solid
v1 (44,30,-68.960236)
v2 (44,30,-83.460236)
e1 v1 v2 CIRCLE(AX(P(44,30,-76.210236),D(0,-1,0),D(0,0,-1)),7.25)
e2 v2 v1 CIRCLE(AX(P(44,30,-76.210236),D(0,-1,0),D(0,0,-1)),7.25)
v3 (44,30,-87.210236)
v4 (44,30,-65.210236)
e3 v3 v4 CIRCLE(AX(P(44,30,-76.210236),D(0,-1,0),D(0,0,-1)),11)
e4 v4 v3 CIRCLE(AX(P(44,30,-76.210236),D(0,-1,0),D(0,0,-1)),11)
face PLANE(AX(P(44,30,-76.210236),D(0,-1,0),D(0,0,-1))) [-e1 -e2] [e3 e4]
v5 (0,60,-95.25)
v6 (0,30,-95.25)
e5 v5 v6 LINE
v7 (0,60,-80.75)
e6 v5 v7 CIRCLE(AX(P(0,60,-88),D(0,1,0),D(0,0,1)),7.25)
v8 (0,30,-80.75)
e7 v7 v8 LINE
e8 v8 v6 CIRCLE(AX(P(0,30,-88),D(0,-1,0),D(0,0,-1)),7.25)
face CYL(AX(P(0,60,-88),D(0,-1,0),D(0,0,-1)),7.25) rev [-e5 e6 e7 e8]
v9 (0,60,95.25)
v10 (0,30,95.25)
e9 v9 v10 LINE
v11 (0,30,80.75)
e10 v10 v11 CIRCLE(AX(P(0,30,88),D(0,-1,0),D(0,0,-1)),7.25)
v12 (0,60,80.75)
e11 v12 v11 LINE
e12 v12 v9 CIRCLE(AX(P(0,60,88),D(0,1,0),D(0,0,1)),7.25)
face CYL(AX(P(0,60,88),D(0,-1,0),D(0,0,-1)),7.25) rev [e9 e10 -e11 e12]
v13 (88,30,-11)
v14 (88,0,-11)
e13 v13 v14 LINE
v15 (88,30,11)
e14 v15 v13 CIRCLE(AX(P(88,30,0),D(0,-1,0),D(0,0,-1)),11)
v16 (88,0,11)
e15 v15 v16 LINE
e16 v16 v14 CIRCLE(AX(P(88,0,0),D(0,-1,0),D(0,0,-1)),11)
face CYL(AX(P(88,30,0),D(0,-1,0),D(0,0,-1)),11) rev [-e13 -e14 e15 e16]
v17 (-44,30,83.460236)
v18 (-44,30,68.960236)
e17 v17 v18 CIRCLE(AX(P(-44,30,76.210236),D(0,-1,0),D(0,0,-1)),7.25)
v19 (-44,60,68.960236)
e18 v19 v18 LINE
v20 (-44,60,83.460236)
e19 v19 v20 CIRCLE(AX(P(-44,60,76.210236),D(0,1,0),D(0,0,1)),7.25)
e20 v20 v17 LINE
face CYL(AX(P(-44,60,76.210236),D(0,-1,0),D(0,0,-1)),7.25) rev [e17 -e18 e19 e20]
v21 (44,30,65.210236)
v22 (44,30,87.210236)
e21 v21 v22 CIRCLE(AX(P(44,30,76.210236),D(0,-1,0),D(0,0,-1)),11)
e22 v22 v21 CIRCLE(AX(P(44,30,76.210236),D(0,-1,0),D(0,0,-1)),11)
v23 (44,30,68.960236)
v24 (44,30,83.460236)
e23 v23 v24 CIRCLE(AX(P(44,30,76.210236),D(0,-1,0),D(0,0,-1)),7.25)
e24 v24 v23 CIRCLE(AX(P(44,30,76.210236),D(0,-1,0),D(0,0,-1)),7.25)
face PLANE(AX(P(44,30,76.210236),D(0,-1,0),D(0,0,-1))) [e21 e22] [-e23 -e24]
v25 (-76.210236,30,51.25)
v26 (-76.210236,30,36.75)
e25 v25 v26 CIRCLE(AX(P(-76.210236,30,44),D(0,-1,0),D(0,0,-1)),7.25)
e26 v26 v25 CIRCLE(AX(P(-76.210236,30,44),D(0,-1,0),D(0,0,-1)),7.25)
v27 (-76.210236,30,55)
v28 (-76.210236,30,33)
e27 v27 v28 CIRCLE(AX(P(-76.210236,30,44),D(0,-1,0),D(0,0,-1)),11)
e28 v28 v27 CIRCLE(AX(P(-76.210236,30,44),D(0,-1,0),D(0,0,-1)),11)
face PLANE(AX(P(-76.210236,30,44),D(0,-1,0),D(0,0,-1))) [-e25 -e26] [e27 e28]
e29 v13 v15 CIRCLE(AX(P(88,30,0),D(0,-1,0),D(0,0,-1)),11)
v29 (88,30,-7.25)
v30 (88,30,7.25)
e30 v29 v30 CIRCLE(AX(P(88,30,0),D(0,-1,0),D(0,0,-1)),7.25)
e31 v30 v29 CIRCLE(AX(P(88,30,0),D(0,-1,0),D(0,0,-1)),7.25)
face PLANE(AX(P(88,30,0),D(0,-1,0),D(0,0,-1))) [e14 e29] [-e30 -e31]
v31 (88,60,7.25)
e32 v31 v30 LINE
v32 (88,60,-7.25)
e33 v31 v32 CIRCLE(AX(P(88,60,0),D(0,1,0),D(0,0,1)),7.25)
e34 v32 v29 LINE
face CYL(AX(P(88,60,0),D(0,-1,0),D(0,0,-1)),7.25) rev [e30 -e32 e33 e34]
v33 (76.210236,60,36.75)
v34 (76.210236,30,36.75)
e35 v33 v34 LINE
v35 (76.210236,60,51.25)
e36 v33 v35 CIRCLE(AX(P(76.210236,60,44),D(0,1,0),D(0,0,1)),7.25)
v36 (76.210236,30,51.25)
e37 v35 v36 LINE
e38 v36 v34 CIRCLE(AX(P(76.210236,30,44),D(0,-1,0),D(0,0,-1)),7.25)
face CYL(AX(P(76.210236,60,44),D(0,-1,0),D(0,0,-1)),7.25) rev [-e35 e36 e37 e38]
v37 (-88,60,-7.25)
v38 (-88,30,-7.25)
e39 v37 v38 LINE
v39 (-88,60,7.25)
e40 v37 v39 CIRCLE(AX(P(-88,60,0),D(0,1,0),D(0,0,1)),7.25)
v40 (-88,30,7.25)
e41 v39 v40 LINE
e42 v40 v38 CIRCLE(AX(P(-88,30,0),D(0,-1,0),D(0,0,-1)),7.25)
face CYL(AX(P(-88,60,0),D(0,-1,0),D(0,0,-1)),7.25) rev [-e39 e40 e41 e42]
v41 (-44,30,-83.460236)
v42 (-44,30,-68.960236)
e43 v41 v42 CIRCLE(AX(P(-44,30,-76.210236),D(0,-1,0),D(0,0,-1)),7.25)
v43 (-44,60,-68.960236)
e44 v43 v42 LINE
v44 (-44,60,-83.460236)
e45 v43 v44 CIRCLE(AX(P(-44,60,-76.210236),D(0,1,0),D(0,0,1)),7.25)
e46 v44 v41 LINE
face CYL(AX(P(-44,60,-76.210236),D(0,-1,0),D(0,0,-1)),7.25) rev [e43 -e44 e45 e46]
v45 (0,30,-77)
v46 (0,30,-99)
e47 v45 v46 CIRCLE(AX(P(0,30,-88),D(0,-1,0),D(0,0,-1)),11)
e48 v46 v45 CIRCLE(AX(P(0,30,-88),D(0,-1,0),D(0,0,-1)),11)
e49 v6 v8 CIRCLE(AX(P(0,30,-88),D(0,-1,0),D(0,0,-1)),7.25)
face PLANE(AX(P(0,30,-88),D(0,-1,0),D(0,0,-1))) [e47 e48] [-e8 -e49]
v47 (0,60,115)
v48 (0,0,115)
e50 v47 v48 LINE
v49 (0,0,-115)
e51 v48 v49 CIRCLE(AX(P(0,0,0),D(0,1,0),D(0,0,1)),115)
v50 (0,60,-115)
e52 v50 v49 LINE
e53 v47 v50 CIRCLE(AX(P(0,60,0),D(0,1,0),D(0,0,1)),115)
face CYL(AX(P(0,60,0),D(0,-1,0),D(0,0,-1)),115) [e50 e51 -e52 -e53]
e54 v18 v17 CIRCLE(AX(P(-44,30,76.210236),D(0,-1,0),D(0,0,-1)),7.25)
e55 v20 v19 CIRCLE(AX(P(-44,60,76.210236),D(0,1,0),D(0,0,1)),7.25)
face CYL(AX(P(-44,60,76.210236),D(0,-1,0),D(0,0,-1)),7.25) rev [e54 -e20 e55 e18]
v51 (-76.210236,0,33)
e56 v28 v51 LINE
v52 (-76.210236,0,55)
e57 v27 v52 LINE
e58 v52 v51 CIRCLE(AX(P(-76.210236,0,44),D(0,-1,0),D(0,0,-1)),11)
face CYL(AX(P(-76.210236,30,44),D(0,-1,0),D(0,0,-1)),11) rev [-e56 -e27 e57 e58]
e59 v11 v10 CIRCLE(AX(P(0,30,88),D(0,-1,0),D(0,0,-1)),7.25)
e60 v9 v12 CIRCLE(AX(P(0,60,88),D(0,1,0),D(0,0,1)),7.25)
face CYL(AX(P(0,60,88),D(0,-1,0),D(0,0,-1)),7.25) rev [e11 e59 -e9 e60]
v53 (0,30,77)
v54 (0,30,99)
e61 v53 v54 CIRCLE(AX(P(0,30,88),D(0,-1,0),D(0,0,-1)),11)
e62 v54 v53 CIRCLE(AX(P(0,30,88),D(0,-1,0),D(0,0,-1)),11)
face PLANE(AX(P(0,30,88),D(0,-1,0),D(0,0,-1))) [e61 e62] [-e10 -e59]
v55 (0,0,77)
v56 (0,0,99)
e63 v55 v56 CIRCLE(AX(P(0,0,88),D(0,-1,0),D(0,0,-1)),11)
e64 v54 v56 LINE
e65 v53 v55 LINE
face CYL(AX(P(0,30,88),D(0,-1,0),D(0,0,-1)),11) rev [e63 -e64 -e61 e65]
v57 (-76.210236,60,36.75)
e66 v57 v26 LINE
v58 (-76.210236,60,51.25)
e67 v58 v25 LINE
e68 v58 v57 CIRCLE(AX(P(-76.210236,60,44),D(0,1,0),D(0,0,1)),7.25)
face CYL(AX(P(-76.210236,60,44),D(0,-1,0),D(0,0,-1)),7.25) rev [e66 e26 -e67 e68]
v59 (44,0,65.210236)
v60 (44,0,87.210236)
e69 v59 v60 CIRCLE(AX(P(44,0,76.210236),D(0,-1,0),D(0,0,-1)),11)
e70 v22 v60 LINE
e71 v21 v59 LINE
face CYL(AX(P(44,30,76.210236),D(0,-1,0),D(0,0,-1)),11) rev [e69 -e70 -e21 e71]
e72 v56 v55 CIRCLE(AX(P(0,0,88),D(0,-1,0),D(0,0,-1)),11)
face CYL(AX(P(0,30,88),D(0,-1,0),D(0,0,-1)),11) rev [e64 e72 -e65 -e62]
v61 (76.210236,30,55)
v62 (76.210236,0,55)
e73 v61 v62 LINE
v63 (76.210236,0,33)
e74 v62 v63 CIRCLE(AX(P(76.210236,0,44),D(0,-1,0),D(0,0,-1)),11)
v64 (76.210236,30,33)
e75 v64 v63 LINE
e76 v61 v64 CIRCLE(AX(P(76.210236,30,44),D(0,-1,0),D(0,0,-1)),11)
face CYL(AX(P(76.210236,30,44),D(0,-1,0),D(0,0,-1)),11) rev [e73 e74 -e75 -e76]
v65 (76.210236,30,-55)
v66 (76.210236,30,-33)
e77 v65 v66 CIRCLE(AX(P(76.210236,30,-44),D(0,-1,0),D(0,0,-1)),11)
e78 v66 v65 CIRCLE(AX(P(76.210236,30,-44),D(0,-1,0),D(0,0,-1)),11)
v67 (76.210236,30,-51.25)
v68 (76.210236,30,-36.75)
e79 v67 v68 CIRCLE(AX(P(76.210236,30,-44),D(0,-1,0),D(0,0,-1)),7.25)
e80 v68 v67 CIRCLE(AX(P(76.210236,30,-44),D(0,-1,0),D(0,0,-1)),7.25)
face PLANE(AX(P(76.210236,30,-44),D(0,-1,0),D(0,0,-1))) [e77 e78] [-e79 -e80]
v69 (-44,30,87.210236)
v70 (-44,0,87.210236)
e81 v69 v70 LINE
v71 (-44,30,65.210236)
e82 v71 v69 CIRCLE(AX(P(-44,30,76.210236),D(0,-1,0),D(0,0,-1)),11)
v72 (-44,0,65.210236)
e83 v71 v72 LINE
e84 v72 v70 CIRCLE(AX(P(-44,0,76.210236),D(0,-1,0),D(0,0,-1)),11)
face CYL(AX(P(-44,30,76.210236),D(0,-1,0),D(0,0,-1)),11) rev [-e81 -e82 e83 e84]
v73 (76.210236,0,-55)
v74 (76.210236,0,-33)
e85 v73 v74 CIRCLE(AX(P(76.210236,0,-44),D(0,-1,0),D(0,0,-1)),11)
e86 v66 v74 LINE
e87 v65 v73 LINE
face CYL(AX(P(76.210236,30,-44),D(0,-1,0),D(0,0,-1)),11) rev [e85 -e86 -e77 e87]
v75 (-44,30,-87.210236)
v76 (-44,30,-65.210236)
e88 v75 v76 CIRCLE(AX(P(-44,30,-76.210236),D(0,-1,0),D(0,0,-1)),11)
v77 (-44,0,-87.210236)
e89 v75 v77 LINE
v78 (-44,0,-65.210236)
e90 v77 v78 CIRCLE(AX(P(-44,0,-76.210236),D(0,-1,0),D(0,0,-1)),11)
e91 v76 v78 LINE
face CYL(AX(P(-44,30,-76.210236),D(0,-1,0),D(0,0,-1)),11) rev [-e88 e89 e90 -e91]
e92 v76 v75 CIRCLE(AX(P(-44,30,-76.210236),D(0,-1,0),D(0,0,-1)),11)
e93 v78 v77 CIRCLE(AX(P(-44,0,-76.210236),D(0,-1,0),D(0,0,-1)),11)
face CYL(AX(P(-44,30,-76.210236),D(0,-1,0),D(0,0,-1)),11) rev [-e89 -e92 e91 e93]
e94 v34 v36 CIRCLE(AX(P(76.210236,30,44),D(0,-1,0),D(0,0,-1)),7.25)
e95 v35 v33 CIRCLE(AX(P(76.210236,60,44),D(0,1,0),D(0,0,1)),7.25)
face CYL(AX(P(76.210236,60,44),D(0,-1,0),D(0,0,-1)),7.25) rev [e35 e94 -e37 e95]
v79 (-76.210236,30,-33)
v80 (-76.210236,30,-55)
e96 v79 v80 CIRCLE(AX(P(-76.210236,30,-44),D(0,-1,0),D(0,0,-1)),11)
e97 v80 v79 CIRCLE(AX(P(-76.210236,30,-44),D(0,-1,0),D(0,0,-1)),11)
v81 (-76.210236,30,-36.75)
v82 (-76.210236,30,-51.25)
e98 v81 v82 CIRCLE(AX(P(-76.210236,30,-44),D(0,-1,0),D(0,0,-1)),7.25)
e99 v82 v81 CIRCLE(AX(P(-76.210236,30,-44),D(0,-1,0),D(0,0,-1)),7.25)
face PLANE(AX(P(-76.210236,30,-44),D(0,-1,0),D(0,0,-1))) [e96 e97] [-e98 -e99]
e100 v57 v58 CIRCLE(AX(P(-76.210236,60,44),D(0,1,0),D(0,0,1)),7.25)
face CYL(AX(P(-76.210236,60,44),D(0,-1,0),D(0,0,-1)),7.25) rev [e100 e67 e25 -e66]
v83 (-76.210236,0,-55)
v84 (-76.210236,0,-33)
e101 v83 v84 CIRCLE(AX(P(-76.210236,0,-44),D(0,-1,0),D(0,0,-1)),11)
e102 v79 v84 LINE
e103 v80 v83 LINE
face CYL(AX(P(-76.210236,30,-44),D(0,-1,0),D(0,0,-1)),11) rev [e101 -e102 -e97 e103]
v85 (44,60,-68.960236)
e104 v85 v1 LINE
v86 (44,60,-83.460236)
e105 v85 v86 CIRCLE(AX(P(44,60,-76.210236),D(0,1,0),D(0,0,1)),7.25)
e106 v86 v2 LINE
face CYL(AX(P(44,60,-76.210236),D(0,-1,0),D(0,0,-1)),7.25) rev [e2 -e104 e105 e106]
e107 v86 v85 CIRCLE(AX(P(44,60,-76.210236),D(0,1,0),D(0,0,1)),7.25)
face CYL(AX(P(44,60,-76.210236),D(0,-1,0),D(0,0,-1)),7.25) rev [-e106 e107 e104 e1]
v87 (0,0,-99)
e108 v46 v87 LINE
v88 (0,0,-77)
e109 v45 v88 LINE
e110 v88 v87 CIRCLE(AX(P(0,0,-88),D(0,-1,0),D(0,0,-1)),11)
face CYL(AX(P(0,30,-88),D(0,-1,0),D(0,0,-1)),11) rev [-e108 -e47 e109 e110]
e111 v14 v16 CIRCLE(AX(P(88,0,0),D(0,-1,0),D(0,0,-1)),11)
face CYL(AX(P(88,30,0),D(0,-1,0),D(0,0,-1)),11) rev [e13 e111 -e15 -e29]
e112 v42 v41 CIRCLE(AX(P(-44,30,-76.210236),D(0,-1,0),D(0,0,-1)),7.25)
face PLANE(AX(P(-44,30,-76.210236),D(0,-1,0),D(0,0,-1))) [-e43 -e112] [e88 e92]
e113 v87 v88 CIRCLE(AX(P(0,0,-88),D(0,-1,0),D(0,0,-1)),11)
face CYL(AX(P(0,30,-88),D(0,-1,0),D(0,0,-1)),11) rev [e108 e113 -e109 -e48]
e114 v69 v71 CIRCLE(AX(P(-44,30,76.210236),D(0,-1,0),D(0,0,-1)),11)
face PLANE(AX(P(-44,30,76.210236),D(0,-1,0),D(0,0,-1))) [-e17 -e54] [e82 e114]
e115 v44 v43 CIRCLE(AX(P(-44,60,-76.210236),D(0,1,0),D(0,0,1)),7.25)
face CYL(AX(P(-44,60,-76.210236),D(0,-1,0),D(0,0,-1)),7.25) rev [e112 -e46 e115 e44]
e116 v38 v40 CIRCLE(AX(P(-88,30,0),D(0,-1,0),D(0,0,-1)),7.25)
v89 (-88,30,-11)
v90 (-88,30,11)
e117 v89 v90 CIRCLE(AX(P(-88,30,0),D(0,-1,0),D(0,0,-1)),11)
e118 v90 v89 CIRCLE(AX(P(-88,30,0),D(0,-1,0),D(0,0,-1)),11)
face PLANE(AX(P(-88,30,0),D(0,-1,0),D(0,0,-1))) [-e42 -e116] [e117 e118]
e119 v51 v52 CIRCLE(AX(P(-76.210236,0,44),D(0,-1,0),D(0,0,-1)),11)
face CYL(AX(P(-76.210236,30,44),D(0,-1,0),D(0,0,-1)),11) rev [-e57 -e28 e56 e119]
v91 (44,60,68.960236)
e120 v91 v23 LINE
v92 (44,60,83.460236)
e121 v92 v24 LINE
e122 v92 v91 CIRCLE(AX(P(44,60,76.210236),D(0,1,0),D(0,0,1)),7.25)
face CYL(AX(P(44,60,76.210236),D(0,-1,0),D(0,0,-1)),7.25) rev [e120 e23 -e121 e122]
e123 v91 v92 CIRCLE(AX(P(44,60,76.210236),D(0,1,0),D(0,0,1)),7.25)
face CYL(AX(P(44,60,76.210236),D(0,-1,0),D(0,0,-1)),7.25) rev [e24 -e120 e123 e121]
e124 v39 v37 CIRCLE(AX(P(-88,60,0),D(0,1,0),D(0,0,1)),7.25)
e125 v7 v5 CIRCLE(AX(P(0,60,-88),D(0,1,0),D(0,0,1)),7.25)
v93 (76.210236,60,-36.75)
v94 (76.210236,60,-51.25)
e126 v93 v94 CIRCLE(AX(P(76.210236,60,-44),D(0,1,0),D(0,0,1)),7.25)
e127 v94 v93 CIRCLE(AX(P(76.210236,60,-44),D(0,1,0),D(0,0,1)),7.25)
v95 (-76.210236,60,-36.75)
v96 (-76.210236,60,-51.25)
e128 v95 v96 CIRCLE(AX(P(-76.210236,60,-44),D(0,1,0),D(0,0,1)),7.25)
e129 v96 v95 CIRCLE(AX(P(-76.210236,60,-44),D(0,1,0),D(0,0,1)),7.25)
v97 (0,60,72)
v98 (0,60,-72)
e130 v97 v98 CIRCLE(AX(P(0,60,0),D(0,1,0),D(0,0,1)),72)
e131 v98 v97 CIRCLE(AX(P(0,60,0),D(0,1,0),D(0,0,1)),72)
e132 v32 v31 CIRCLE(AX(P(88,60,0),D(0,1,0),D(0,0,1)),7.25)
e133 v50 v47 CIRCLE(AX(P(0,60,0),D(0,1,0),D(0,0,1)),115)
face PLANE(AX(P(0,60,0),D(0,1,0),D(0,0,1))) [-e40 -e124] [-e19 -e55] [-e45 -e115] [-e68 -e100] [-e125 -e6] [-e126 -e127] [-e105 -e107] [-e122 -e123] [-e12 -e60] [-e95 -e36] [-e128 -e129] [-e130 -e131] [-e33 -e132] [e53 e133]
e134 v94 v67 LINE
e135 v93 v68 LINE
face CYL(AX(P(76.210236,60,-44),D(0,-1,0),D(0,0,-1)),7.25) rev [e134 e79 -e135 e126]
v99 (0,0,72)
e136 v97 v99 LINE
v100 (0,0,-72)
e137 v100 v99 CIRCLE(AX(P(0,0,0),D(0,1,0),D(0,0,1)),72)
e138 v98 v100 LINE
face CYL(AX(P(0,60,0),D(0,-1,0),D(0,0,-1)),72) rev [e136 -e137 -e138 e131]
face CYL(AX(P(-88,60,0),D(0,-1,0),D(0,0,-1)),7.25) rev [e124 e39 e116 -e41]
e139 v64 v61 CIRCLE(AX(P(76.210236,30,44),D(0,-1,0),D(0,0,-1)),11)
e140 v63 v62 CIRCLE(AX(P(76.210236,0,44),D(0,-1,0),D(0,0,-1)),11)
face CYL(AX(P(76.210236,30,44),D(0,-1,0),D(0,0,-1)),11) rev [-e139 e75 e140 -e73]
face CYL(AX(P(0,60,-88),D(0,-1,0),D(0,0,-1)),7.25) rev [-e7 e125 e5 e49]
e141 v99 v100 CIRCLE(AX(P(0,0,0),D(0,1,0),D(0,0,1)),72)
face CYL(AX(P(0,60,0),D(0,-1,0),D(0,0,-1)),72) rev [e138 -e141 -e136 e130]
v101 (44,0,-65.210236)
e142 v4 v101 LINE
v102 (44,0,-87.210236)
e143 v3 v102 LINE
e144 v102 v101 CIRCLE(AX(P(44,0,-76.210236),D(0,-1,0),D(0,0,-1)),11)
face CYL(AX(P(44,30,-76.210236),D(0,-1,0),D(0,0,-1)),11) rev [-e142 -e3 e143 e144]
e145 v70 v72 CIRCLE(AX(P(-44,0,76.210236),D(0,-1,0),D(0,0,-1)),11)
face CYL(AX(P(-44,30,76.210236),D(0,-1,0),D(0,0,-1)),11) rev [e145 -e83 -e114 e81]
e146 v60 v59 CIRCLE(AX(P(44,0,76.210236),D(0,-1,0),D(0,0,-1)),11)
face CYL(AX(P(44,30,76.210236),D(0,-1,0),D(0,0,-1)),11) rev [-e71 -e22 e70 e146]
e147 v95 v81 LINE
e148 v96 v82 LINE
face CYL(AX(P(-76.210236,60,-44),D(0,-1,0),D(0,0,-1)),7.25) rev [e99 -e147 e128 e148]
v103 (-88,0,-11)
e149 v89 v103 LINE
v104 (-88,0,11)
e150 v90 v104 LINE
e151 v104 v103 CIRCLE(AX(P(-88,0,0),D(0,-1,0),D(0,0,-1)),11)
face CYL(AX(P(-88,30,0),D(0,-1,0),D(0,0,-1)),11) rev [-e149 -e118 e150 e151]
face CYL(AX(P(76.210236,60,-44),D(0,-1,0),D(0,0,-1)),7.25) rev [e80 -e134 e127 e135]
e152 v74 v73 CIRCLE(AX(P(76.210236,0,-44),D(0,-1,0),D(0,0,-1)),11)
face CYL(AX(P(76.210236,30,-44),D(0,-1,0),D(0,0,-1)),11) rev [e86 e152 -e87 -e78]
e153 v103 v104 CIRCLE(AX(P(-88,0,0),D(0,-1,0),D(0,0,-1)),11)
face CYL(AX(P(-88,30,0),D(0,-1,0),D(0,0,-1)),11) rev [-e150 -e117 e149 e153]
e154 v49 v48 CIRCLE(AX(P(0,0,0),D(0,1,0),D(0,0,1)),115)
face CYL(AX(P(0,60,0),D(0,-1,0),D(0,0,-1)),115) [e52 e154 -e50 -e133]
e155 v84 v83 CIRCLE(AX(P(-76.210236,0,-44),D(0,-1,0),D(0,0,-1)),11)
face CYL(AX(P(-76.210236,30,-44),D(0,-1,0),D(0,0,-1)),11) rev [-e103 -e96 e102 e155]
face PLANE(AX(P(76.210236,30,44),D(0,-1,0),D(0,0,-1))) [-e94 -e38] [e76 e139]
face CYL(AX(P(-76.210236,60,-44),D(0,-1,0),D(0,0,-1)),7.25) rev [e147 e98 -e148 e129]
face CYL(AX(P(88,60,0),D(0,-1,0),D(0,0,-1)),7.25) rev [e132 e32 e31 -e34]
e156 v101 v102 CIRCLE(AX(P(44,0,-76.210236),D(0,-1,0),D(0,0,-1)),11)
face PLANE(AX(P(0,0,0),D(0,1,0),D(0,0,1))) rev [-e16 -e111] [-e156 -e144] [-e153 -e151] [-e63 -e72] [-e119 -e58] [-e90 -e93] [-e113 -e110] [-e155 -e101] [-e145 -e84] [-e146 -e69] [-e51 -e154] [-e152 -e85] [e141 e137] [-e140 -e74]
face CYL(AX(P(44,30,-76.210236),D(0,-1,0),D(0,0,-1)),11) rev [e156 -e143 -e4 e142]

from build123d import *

# Parameters (mm, degrees)
SKETCH1_R           = 115
SKETCH1_R_2         = 72
SKETCH1_R_3         = 7.25
BOSS_EXTRUDE1_DEPTH = 60
SKETCH2_R           = 11
CUT_EXTRUDE1_DEPTH  = 30


with BuildPart() as part:
    # Sketch1 → Boss-Extrude1 (new body)
    with BuildSketch(Plane(origin=(0, 0, 0), x_dir=(1, 0, 0), z_dir=(0, 1, 0))):
        with Locations(Location((0, 0, 0), (0, 0, 270))):
            Circle(SKETCH1_R)
        with Locations(Location((0, 0, 0), (0, 0, 270))):
            Circle(SKETCH1_R_2, mode=Mode.SUBTRACT)
        with Locations(Location((0, 88, 0), (0, 0, 270))):
            Circle(SKETCH1_R_3, mode=Mode.SUBTRACT)
        with Locations(Location((44, 76.210235533, 0), (0, 0, 270))):
            Circle(SKETCH1_R_3, mode=Mode.SUBTRACT)
        with Locations(Location((76.210235533, 44, 0), (0, 0, 270))):
            Circle(SKETCH1_R_3, mode=Mode.SUBTRACT)
        with Locations(Location((88, 0, 0), (0, 0, 270))):
            Circle(SKETCH1_R_3, mode=Mode.SUBTRACT)
        with Locations(Location((76.210235533, -44, 0), (0, 0, 270))):
            Circle(SKETCH1_R_3, mode=Mode.SUBTRACT)
        with Locations(Location((44, -76.210235533, 0), (0, 0, 270))):
            Circle(SKETCH1_R_3, mode=Mode.SUBTRACT)
        with Locations(Location((0, -88, 0), (0, 0, 270))):
            Circle(SKETCH1_R_3, mode=Mode.SUBTRACT)
        with Locations(Location((-44, -76.210235533, 0), (0, 0, 270))):
            Circle(SKETCH1_R_3, mode=Mode.SUBTRACT)
        with Locations(Location((-76.210235533, -44, 0), (0, 0, 270))):
            Circle(SKETCH1_R_3, mode=Mode.SUBTRACT)
        with Locations(Location((-88, 0, 0), (0, 0, 270))):
            Circle(SKETCH1_R_3, mode=Mode.SUBTRACT)
        with Locations(Location((-76.210235533, 44, 0), (0, 0, 270))):
            Circle(SKETCH1_R_3, mode=Mode.SUBTRACT)
        with Locations(Location((-44, 76.210235533, 0), (0, 0, 270))):
            Circle(SKETCH1_R_3, mode=Mode.SUBTRACT)
    extrude(amount=BOSS_EXTRUDE1_DEPTH)

    # Sketch2 → Cut-Extrude1 (cut)
    with BuildSketch(Plane.XZ):
        with Locations(Location((0, 88, 0), (0, 0, 270))):
            Circle(SKETCH2_R)
        with Locations(Location((44, 76.210235533, 0), (0, 0, 270))):
            Circle(SKETCH2_R)
        with Locations(Location((76.210235533, 44, 0), (0, 0, 270))):
            Circle(SKETCH2_R)
        with Locations(Location((88, 0, 0), (0, 0, 270))):
            Circle(SKETCH2_R)
        with Locations(Location((76.210235533, -44, 0), (0, 0, 270))):
            Circle(SKETCH2_R)
        with Locations(Location((44, -76.210235533, 0), (0, 0, 270))):
            Circle(SKETCH2_R)
        with Locations(Location((0, -88, 0), (0, 0, 270))):
            Circle(SKETCH2_R)
        with Locations(Location((-44, -76.210235533, 0), (0, 0, 270))):
            Circle(SKETCH2_R)
        with Locations(Location((-76.210235533, -44, 0), (0, 0, 270))):
            Circle(SKETCH2_R)
        with Locations(Location((-88, 0, 0), (0, 0, 270))):
            Circle(SKETCH2_R)
        with Locations(Location((-76.210235533, 44, 0), (0, 0, 270))):
            Circle(SKETCH2_R)
        with Locations(Location((-44, 76.210235533, 0), (0, 0, 270))):
            Circle(SKETCH2_R)
    extrude(amount=-CUT_EXTRUDE1_DEPTH, mode=Mode.SUBTRACT)


solid = part.part
